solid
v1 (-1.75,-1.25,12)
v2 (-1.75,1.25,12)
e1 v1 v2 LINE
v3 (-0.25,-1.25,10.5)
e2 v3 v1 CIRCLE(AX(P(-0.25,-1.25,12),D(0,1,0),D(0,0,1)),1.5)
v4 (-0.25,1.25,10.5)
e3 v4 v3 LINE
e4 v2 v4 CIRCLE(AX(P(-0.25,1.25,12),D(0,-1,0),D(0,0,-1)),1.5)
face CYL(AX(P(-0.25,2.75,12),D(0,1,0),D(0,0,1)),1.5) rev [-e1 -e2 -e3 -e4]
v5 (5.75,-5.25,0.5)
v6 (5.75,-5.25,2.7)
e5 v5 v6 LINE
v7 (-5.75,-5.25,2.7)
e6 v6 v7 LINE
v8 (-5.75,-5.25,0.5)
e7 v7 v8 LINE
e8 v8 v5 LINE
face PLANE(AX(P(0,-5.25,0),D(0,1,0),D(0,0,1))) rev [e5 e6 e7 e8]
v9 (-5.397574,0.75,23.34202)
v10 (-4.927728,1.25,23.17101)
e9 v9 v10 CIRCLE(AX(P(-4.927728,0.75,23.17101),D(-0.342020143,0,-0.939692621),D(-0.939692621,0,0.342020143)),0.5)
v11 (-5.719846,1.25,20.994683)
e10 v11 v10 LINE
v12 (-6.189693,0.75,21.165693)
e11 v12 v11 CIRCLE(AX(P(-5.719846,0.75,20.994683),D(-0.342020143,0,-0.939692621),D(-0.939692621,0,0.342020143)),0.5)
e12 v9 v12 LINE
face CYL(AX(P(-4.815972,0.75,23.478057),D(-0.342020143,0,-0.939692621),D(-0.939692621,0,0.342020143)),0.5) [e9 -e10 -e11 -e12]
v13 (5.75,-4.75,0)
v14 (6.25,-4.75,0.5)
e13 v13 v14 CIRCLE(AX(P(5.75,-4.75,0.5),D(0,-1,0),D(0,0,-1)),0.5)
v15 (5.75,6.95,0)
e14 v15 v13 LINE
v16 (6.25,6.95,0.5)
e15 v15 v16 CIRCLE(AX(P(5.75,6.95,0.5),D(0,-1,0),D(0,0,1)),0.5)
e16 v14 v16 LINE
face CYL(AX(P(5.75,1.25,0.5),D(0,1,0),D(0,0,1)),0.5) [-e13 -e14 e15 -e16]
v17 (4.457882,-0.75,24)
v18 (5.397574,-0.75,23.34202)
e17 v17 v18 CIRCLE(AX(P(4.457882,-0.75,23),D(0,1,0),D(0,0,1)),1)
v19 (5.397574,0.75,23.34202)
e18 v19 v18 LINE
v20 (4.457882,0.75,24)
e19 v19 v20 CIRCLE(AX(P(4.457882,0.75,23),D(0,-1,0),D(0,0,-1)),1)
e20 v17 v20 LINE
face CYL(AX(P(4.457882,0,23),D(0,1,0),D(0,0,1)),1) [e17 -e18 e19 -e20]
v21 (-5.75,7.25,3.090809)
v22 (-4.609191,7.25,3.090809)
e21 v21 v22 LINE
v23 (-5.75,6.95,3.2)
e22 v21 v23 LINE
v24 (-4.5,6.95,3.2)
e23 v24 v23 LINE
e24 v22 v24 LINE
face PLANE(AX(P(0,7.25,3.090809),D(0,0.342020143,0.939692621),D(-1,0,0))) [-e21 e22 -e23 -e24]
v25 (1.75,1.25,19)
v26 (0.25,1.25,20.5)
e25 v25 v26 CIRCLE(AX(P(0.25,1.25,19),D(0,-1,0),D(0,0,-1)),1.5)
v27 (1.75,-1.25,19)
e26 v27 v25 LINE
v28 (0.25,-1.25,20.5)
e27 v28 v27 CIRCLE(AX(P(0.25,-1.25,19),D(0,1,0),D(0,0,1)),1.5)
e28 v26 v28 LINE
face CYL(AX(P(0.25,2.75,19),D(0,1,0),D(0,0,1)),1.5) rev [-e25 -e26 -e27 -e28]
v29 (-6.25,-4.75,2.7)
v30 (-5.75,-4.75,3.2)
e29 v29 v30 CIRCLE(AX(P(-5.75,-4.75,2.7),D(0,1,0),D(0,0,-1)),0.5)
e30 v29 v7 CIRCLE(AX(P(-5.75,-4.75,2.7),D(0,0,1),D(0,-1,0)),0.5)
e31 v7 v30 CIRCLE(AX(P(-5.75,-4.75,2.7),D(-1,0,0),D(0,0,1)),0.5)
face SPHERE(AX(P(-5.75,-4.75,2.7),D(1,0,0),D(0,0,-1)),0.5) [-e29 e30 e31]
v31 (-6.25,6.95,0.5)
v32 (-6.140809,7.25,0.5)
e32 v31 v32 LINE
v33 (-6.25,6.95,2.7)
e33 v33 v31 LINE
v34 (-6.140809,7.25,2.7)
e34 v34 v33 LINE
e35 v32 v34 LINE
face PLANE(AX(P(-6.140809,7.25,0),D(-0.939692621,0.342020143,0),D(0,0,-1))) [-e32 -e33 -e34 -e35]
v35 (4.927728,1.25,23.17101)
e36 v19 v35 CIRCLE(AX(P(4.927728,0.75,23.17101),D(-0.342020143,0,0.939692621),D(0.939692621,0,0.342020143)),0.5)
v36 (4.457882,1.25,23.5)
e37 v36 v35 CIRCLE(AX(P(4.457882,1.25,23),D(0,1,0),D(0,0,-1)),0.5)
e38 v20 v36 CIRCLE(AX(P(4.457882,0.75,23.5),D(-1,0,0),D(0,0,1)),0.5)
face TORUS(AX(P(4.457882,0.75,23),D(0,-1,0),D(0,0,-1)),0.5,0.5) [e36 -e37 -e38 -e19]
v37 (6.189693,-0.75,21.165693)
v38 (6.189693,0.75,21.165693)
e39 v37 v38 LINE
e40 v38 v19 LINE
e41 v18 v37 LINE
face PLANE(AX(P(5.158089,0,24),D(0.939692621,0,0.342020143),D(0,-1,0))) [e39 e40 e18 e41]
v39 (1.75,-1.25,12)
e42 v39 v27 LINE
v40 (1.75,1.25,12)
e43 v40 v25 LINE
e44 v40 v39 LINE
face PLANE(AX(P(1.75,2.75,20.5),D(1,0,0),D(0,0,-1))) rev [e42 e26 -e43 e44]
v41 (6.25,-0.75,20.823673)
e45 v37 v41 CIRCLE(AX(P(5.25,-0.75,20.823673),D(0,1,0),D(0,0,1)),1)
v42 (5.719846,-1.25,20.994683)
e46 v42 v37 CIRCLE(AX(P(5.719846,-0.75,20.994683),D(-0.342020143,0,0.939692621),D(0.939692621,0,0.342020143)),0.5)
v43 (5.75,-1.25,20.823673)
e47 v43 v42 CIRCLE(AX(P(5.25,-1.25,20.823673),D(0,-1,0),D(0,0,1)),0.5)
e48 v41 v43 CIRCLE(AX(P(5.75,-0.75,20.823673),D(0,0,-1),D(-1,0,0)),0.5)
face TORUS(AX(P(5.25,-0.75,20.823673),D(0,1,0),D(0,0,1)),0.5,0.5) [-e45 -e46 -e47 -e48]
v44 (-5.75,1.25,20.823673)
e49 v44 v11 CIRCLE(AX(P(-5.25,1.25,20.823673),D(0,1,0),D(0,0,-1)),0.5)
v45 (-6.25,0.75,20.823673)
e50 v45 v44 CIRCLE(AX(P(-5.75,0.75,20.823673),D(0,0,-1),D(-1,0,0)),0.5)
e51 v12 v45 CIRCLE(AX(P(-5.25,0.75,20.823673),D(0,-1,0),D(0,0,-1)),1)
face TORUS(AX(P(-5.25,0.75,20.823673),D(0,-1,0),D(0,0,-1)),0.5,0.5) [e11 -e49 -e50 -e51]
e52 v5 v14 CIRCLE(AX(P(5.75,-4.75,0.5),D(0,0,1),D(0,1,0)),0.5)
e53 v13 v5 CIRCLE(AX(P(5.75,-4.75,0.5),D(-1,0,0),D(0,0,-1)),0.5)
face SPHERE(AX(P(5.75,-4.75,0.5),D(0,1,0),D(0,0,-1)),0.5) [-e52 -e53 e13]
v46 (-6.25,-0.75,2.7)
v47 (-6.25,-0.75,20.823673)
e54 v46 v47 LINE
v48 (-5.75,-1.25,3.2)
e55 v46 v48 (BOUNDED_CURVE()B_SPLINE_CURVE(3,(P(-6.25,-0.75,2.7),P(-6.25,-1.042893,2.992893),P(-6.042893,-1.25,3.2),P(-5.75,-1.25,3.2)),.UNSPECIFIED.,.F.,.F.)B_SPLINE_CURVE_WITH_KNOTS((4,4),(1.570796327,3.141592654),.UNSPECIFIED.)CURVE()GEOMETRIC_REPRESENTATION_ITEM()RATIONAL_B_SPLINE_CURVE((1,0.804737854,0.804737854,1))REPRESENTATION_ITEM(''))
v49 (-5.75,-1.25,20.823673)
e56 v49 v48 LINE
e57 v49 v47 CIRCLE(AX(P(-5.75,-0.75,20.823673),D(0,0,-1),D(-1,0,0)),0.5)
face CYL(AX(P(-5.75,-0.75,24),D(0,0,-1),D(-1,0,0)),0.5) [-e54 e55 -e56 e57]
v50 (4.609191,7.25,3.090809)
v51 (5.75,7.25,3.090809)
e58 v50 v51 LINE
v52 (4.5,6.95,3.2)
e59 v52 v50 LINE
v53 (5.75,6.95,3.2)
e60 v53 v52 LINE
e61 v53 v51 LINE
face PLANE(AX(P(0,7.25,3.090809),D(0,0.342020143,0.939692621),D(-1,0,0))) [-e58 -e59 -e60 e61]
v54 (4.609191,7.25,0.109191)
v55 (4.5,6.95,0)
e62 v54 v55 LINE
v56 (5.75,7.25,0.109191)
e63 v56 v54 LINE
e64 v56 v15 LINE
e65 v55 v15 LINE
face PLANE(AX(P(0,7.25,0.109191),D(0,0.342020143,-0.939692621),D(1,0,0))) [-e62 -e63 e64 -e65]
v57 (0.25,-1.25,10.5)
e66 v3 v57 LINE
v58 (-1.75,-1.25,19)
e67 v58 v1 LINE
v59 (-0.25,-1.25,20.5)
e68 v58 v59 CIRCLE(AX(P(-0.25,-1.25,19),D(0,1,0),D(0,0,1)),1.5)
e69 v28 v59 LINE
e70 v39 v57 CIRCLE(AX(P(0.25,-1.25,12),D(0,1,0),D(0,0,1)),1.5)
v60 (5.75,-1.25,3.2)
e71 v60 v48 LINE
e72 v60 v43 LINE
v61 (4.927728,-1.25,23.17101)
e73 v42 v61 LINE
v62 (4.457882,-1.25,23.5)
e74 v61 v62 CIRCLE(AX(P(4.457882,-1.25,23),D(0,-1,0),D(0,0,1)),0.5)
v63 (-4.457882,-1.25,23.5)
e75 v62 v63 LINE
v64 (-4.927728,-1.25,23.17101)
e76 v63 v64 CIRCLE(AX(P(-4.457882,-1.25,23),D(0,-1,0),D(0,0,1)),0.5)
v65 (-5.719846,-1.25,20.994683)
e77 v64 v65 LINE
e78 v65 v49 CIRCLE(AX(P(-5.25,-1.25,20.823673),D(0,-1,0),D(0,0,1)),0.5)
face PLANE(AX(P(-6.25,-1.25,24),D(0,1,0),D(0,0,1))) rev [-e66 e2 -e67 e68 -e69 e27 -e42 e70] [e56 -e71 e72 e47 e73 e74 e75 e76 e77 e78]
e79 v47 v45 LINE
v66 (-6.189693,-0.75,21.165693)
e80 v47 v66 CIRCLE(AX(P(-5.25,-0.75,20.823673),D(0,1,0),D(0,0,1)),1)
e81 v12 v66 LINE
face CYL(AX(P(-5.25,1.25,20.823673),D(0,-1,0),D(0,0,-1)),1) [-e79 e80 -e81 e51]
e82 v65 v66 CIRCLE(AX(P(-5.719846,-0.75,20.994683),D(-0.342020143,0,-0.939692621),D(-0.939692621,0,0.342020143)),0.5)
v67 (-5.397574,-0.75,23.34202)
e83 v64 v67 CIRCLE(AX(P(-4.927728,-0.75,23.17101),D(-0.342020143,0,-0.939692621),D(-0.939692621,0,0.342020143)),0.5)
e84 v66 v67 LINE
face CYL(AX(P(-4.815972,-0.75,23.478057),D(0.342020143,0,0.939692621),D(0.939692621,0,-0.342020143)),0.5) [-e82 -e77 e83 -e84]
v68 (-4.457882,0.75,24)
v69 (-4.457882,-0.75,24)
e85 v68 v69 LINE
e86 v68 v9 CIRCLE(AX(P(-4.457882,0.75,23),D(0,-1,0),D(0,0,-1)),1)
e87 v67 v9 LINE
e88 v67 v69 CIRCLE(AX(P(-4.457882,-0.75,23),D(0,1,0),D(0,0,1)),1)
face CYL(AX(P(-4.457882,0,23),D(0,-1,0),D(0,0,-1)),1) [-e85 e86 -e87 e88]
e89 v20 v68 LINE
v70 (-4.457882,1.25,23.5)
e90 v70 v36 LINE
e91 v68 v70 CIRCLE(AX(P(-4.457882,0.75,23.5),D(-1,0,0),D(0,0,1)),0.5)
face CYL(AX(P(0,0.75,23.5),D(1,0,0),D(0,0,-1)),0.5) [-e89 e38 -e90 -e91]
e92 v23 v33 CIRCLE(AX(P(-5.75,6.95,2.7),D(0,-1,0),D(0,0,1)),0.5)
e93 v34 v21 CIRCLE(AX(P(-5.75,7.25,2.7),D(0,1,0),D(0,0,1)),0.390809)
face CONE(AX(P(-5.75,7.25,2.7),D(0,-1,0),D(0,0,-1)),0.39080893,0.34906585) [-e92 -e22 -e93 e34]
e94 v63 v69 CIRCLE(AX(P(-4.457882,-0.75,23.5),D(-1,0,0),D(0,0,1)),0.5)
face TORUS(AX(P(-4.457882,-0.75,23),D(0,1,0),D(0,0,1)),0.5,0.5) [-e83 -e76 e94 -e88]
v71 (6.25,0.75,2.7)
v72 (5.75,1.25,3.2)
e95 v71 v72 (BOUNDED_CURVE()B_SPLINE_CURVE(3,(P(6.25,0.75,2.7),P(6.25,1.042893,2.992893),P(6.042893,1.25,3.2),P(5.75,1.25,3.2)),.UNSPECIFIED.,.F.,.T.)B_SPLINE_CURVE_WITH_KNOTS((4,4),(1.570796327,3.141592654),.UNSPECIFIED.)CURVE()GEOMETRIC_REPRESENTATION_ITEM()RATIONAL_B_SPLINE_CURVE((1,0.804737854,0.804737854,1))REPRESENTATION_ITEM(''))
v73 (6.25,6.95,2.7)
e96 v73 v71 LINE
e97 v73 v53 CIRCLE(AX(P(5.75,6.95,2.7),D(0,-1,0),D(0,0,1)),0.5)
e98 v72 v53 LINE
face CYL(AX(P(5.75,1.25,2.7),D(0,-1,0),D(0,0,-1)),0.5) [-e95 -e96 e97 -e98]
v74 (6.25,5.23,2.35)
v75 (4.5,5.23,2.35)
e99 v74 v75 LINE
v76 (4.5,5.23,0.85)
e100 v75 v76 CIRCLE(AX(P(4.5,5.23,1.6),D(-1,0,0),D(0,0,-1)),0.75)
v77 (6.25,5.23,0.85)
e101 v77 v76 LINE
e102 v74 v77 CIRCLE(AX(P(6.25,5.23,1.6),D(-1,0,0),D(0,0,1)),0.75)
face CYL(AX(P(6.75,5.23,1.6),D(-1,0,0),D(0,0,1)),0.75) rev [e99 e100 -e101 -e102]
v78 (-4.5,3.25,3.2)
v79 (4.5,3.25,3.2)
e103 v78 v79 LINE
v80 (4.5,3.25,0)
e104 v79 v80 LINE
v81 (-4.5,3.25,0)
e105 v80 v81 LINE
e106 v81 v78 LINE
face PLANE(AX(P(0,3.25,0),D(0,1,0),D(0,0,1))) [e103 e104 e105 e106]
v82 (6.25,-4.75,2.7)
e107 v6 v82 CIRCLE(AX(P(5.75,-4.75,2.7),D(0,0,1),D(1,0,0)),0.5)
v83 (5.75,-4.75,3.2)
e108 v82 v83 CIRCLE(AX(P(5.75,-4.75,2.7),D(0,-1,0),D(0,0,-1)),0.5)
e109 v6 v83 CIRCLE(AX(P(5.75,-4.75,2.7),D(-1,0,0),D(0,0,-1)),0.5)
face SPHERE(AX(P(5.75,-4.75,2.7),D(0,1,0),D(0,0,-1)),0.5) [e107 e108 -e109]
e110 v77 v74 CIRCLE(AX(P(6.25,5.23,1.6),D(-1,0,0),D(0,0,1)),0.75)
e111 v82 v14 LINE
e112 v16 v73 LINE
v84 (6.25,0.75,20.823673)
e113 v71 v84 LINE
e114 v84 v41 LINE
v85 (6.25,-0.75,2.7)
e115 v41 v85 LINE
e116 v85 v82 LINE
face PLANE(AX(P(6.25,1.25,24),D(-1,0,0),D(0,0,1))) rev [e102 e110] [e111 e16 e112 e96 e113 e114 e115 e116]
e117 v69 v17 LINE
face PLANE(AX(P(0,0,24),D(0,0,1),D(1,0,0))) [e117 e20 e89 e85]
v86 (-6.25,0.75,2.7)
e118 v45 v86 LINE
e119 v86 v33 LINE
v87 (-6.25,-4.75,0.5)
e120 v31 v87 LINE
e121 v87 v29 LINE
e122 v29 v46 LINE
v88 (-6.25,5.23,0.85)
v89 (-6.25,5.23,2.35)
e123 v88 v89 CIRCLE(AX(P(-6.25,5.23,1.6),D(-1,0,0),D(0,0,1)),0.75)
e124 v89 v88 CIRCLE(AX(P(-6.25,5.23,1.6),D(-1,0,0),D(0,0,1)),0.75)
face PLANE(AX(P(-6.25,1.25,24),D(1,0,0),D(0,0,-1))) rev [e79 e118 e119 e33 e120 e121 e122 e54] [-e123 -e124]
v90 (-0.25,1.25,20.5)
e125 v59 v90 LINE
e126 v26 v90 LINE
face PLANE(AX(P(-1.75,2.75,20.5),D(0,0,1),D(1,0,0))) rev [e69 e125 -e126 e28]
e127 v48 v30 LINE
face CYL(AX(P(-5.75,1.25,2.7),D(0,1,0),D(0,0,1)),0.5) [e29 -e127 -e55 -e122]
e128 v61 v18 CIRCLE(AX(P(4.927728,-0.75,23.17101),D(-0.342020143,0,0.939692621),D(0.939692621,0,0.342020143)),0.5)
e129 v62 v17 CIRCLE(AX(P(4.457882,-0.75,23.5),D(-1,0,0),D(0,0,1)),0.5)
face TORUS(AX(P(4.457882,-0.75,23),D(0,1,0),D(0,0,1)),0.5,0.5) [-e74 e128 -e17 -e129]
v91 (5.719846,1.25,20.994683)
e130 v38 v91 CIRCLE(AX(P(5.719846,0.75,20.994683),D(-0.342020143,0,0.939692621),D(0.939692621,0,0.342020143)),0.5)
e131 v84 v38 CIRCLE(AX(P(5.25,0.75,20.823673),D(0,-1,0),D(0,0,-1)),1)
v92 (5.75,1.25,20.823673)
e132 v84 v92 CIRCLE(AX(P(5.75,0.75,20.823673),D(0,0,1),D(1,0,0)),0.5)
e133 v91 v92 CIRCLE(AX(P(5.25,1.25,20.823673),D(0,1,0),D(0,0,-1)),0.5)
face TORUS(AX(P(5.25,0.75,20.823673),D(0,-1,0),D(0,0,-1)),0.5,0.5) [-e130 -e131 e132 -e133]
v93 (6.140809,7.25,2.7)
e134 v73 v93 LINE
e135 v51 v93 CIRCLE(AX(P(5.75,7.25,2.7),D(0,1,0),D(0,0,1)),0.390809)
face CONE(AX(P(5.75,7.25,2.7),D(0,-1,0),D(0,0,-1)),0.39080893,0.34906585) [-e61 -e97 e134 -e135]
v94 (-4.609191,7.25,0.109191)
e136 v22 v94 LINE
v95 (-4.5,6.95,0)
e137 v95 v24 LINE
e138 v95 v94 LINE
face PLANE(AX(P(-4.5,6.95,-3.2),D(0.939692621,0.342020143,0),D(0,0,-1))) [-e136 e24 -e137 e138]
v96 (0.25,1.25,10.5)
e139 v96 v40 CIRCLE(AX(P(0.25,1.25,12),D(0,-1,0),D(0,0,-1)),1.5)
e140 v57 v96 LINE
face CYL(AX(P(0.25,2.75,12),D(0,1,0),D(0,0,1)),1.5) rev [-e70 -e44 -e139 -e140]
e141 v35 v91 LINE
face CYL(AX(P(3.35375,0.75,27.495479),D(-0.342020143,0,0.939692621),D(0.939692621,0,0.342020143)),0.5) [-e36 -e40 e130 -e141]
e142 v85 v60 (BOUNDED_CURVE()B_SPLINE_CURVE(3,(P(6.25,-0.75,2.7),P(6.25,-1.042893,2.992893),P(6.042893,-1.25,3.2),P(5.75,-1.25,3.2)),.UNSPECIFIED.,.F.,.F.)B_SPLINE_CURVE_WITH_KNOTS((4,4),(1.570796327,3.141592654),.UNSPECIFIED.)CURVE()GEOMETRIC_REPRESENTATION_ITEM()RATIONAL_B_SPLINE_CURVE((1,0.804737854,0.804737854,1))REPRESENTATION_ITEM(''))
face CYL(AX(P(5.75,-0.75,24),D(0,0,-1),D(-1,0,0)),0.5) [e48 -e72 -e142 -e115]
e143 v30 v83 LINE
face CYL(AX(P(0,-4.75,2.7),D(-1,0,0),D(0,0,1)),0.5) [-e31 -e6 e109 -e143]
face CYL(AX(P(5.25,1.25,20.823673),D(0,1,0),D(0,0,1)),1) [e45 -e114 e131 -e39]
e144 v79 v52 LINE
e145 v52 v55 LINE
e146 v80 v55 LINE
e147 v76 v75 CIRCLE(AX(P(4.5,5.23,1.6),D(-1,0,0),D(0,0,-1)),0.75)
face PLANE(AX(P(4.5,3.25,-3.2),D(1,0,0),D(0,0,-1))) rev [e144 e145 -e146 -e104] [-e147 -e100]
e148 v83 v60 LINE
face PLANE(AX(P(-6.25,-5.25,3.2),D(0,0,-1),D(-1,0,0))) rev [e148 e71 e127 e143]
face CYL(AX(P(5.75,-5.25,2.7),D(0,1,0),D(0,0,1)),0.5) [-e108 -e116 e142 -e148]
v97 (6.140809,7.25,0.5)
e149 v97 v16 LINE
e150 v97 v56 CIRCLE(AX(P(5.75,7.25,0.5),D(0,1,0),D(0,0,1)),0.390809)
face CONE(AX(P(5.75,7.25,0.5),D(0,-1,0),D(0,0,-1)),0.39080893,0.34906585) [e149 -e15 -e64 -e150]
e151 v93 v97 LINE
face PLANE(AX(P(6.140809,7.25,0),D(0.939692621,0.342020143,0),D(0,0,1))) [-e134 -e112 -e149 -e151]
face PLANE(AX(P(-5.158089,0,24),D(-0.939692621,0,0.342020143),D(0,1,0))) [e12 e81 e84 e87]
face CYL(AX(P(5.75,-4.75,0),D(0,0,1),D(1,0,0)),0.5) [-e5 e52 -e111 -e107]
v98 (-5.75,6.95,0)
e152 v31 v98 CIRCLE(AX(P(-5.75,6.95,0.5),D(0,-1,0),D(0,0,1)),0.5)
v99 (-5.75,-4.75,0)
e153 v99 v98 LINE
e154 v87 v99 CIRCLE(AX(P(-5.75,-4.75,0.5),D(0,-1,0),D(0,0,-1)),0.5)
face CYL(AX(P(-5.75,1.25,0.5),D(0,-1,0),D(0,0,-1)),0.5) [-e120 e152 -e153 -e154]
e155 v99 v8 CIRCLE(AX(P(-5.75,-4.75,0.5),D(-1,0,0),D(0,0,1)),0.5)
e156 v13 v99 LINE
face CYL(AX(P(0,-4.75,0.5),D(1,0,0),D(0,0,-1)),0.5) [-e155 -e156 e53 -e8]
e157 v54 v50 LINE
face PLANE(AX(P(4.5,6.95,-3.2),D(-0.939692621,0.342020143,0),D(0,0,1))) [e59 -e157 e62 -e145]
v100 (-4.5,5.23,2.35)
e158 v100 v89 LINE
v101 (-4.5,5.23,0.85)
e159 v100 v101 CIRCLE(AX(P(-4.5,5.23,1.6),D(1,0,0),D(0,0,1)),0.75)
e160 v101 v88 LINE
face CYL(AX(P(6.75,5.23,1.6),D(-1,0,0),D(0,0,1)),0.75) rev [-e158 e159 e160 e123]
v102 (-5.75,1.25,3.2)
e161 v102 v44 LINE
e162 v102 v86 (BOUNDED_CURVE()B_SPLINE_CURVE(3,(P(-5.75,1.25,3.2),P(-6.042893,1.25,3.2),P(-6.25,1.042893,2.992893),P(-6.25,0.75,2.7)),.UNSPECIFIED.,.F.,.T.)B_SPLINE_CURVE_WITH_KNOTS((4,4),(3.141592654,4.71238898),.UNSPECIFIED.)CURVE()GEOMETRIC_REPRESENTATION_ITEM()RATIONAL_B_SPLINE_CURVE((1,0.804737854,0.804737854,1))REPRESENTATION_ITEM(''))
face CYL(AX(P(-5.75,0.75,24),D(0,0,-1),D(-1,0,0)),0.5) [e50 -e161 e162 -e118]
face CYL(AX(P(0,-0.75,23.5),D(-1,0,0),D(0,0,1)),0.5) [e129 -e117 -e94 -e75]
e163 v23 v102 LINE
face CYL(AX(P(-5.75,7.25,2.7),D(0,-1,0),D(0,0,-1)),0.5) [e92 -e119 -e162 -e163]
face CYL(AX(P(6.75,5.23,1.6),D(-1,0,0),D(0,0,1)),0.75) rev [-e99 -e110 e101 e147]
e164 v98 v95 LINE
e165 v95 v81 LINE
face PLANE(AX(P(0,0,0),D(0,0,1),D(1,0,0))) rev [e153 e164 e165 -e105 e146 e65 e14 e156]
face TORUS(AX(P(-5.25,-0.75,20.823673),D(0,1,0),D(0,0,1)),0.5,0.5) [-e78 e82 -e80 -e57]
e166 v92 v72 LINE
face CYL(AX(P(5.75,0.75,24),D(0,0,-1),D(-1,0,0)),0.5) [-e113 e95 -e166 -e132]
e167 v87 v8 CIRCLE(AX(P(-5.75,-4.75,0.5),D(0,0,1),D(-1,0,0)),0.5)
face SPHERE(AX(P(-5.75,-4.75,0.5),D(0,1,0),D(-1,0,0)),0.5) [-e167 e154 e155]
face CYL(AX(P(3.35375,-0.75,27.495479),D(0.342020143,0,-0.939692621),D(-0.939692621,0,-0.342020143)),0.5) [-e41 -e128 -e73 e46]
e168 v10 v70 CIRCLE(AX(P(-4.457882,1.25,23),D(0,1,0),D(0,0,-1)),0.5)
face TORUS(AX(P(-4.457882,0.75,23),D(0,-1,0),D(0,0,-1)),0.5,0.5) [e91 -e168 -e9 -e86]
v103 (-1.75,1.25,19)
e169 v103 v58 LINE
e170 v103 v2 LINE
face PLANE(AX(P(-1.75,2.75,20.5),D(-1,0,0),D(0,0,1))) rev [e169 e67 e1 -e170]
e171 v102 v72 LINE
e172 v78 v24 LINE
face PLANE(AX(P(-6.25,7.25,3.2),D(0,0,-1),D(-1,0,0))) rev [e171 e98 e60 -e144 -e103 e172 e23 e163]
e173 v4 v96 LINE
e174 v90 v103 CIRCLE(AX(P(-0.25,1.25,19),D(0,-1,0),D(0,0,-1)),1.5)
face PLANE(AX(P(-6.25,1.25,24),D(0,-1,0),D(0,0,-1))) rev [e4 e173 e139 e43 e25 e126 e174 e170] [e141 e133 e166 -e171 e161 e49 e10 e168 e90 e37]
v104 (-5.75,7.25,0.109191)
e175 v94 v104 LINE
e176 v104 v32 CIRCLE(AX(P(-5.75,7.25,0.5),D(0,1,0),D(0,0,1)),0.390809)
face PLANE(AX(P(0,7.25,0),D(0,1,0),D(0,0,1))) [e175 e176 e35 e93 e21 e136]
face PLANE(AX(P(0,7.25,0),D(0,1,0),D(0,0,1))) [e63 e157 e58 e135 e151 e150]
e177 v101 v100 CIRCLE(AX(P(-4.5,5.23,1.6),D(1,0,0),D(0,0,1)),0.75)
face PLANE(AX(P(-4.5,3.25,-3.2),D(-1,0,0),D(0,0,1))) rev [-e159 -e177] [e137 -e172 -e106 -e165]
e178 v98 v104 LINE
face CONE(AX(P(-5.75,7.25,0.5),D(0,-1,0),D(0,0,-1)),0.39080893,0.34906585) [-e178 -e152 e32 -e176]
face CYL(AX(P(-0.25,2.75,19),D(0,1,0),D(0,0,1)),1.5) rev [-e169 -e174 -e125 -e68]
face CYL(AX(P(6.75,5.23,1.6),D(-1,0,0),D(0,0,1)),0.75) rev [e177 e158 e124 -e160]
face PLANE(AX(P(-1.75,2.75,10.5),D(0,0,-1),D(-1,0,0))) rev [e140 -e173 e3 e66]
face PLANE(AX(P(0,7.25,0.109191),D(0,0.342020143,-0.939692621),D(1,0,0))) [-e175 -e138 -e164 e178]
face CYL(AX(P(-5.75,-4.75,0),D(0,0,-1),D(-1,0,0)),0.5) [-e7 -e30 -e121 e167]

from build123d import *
from OCP.BRepFilletAPI import BRepFilletAPI_MakeChamfer

# Parameters (mm, degrees)
SKETCH1_W           = 12.5
SKETCH1_H           = 2.5
BOSS_EXTRUDE1_DEPTH = 24
SKETCH2_W           = 12.5
SKETCH2_H           = 3.2
BOSS_EXTRUDE2_DEPTH = 6
SKETCH3_R           = 0.75
CUT_EXTRUDE1_DEPTH  = 13
SKETCH4_W           = 9
SKETCH4_H           = 6.4
CUT_EXTRUDE2_DEPTH  = 4
SKETCH5_W           = 12.5
SKETCH5_H           = 3.2
BOSS_EXTRUDE3_DEPTH = 4
SKETCH7_W           = 3.5
SKETCH7_H           = 10
CUT_EXTRUDE3_DEPTH  = 4
FILLET3_R           = 1.5
CHAMFER1_SIZE       = 3
CHAMFER1_SIZE2      = 1.091910703
FILLET1_R           = 1
FILLET2_R           = 0.5
CHAMFER2_SIZE       = 0.3
CHAMFER2_SIZE2      = 0.10919107


with BuildPart() as part:
    # Sketch1 → Boss-Extrude1 (new body)
    with BuildSketch(Plane.XY):
        Rectangle(SKETCH1_W, SKETCH1_H)
    extrude(amount=BOSS_EXTRUDE1_DEPTH)

    # Sketch2 → Boss-Extrude2 (add)
    with BuildSketch(Plane(origin=(0, 1.25, 0), x_dir=(1, 0, 0), z_dir=(0, 1, 0))):
        with Locations((0, -1.6)):
            Rectangle(SKETCH2_W, SKETCH2_H)
    extrude(amount=BOSS_EXTRUDE2_DEPTH)

    # Sketch3 → Cut-Extrude1 (cut)
    with BuildSketch(Plane.ZY.offset(6.25)):
        with Locations((1.6, 5.23)):
            Circle(SKETCH3_R)
    extrude(amount=-CUT_EXTRUDE1_DEPTH, mode=Mode.SUBTRACT)

    # Sketch4 → Cut-Extrude2 (cut)
    with BuildSketch(Plane(origin=(0, 7.25, 0), x_dir=(1, 0, 0), z_dir=(0, 1, 0))):
        Rectangle(SKETCH4_W, SKETCH4_H)
    extrude(amount=-CUT_EXTRUDE2_DEPTH, mode=Mode.SUBTRACT)

    # Sketch5 → Boss-Extrude3 (add)
    with BuildSketch(Plane.XZ.offset(1.25)):
        with Locations((0, 1.6)):
            Rectangle(SKETCH5_W, SKETCH5_H)
    extrude(amount=BOSS_EXTRUDE3_DEPTH)

    # Sketch7 → Cut-Extrude3 (cut)
    with BuildSketch(Plane.XZ.offset(1.25)):
        with Locations((0, 15.5)):
            Rectangle(SKETCH7_W, SKETCH7_H)
    extrude(amount=-CUT_EXTRUDE3_DEPTH, mode=Mode.SUBTRACT)

    # Fillet3
    fillet3_edges = [part.edges().sort_by_distance(p)[0] for p in [
        (1.75, 0, 20.5),
        (1.75, 0, 10.5),
        (-1.75, 0, 10.5),
        (-1.75, 0, 20.5),
    ]]
    fillet(fillet3_edges, radius=FILLET3_R)

    # Chamfer1: one chamfer whose edges measure the first distance from different faces: ONE call of the kernel's chamfer builder (chamfer() names one face for all edges)
    chamfer1_edges_1 = [part.edges().sort_by_distance(p)[0] for p in [
        (-6.25, 0, 24),
    ]]
    chamfer1_side_1 = [part.faces().sort_by_distance(p)[0] for p in [
        (-6.25, 0.340871708, 8.515441233),
    ]]
    chamfer1_edges_2 = [part.edges().sort_by_distance(p)[0] for p in [
        (6.25, 0, 24),
    ]]
    chamfer1_side_2 = [part.faces().sort_by_distance(p)[0] for p in [
        (6.25, 0.340871708, 8.515441233),
    ]]
    chamfer1 = BRepFilletAPI_MakeChamfer(part.part.solid().wrapped)
    for e in chamfer1_edges_1:
        chamfer1.Add(CHAMFER1_SIZE, CHAMFER1_SIZE2, e.wrapped, chamfer1_side_1[0].wrapped)  # the first distance lies on this face
    for e in chamfer1_edges_2:
        chamfer1.Add(CHAMFER1_SIZE, CHAMFER1_SIZE2, e.wrapped, chamfer1_side_2[0].wrapped)  # the first distance lies on this face
    add(Compound.cast(chamfer1.Shape()), mode=Mode.REPLACE)

    # Fillet1
    fillet1_edges = [part.edges().sort_by_distance(p)[0] for p in [
        (-5.158089297, 0, 24),
        (5.158089297, 0, 24),
        (6.25, 0, 21),
        (-6.25, 0, 21),
    ]]
    fillet(fillet1_edges, radius=FILLET1_R)

    # Fillet2
    fillet2_edges = [part.edges().sort_by_distance(p)[0] for p in [
        (6.25, 1.25, 12.01183651),
        (6.25, -1.25, 12.01183651),
        (5.7936335, -1.25, 22.253856653),
        (0, -1.25, 24),
        (-5.7936335, -1.25, 22.253856653),
        (-6.25, -1.25, 12.01183651),
        (-5.031458195, -1.25, 23.819152044),
        (-6.234807753, -1.25, 20.997321197),
        (5.031458195, -1.25, 23.819152044),
        (6.234807753, -1.25, 20.997321197),
        (5.7936335, 1.25, 22.253856653),
        (0, 1.25, 24),
        (-6.25, 1.25, 12.01183651),
        (-5.7936335, 1.25, 22.253856653),
        (-5.031458195, 1.25, 23.819152044),
        (-6.234807753, 1.25, 20.997321197),
        (5.031458195, 1.25, 23.819152044),
        (6.234807753, 1.25, 20.997321197),
        (-6.25, 4.25, 3.2),
        (6.25, 4.25, 3.2),
        (-6.25, 1, 0),
        (-6.25, -3.25, 3.2),
        (6.25, -3.25, 3.2),
        (-6.25, -5.25, 1.6),
        (0, -5.25, 0),
        (6.25, -5.25, 1.6),
        (0, -5.25, 3.2),
        (6.25, 1, 0),
    ]]
    fillet(fillet2_edges, radius=FILLET2_R)

    # Chamfer2: one chamfer whose edges measure the first distance from different faces: ONE call of the kernel's chamfer builder (chamfer() names one face for all edges)
    chamfer2_edges_1 = [part.edges().sort_by_distance(p)[0] for p in [
        (-6.25, 7.25, 1.6),
    ]]
    chamfer2_side_1 = [part.faces().sort_by_distance(p)[0] for p in [
        (-6.25, 0.458482774, 6.931212407),
    ]]
    chamfer2_edges_2 = [part.edges().sort_by_distance(p)[0] for p in [
        (6.25, 7.25, 1.6),
    ]]
    chamfer2_side_2 = [part.faces().sort_by_distance(p)[0] for p in [
        (6.25, 0.458482774, 6.931212407),
    ]]
    chamfer2_edges_3 = [part.edges().sort_by_distance(p)[0] for p in [
        (5.125, 7.25, 0),
        (-5.125, 7.25, 0),
    ]]
    chamfer2_side_3 = [part.faces().sort_by_distance(p)[0] for p in [
        (0, -0.161764706, 0),
    ]]
    chamfer2_edges_4 = [part.edges().sort_by_distance(p)[0] for p in [
        (-5.125, 7.25, 3.2),
        (5.125, 7.25, 3.2),
    ]]
    chamfer2_side_4 = [part.faces().sort_by_distance(p)[0] for p in [
        (0, 3.159090909, 3.2),
    ]]
    chamfer2_edges_5 = [part.edges().sort_by_distance(p)[0] for p in [
        (6.103553391, 7.25, 0.146446609),
    ]]
    chamfer2_side_5 = [part.faces().sort_by_distance(p)[0] for p in [
        (6.103553391, 1.25, 0.146446609),
    ]]
    chamfer2_edges_6 = [part.edges().sort_by_distance(p)[0] for p in [
        (6.103553391, 7.25, 3.053553391),
    ]]
    chamfer2_side_6 = [part.faces().sort_by_distance(p)[0] for p in [
        (6.103553391, 4, 3.053553391),
    ]]
    chamfer2_edges_7 = [part.edges().sort_by_distance(p)[0] for p in [
        (-6.103553391, 7.25, 3.053553391),
    ]]
    chamfer2_side_7 = [part.faces().sort_by_distance(p)[0] for p in [
        (-6.103553391, 4, 3.053553391),
    ]]
    chamfer2_edges_8 = [part.edges().sort_by_distance(p)[0] for p in [
        (-6.103553391, 7.25, 0.146446609),
    ]]
    chamfer2_side_8 = [part.faces().sort_by_distance(p)[0] for p in [
        (-6.103553391, 1.25, 0.146446609),
    ]]
    chamfer2_edges_9 = [part.edges().sort_by_distance(p)[0] for p in [
        (4.5, 7.25, 1.6),
    ]]
    chamfer2_side_9 = [part.faces().sort_by_distance(p)[0] for p in [
        (4.5, 7.198775006, 1.6),
    ]]
    chamfer2_edges_10 = [part.edges().sort_by_distance(p)[0] for p in [
        (-4.5, 7.25, 1.6),
    ]]
    chamfer2_side_10 = [part.faces().sort_by_distance(p)[0] for p in [
        (-4.5, 7.198775006, 1.6),
    ]]
    chamfer2 = BRepFilletAPI_MakeChamfer(part.part.solid().wrapped)
    for e in chamfer2_edges_1:
        chamfer2.Add(CHAMFER2_SIZE, CHAMFER2_SIZE2, e.wrapped, chamfer2_side_1[0].wrapped)  # the first distance lies on this face
    for e in chamfer2_edges_2:
        chamfer2.Add(CHAMFER2_SIZE, CHAMFER2_SIZE2, e.wrapped, chamfer2_side_2[0].wrapped)  # the first distance lies on this face
    for e in chamfer2_edges_3:
        chamfer2.Add(CHAMFER2_SIZE, CHAMFER2_SIZE2, e.wrapped, chamfer2_side_3[0].wrapped)  # the first distance lies on this face
    for e in chamfer2_edges_4:
        chamfer2.Add(CHAMFER2_SIZE, CHAMFER2_SIZE2, e.wrapped, chamfer2_side_4[0].wrapped)  # the first distance lies on this face
    for e in chamfer2_edges_5:
        chamfer2.Add(CHAMFER2_SIZE, CHAMFER2_SIZE2, e.wrapped, chamfer2_side_5[0].wrapped)  # the first distance lies on this face
    for e in chamfer2_edges_6:
        chamfer2.Add(CHAMFER2_SIZE, CHAMFER2_SIZE2, e.wrapped, chamfer2_side_6[0].wrapped)  # the first distance lies on this face
    for e in chamfer2_edges_7:
        chamfer2.Add(CHAMFER2_SIZE, CHAMFER2_SIZE2, e.wrapped, chamfer2_side_7[0].wrapped)  # the first distance lies on this face
    for e in chamfer2_edges_8:
        chamfer2.Add(CHAMFER2_SIZE, CHAMFER2_SIZE2, e.wrapped, chamfer2_side_8[0].wrapped)  # the first distance lies on this face
    for e in chamfer2_edges_9:
        chamfer2.Add(CHAMFER2_SIZE, CHAMFER2_SIZE2, e.wrapped, chamfer2_side_9[0].wrapped)  # the first distance lies on this face
    for e in chamfer2_edges_10:
        chamfer2.Add(CHAMFER2_SIZE, CHAMFER2_SIZE2, e.wrapped, chamfer2_side_10[0].wrapped)  # the first distance lies on this face
    add(Compound.cast(chamfer2.Shape()), mode=Mode.REPLACE)


solid = part.part
